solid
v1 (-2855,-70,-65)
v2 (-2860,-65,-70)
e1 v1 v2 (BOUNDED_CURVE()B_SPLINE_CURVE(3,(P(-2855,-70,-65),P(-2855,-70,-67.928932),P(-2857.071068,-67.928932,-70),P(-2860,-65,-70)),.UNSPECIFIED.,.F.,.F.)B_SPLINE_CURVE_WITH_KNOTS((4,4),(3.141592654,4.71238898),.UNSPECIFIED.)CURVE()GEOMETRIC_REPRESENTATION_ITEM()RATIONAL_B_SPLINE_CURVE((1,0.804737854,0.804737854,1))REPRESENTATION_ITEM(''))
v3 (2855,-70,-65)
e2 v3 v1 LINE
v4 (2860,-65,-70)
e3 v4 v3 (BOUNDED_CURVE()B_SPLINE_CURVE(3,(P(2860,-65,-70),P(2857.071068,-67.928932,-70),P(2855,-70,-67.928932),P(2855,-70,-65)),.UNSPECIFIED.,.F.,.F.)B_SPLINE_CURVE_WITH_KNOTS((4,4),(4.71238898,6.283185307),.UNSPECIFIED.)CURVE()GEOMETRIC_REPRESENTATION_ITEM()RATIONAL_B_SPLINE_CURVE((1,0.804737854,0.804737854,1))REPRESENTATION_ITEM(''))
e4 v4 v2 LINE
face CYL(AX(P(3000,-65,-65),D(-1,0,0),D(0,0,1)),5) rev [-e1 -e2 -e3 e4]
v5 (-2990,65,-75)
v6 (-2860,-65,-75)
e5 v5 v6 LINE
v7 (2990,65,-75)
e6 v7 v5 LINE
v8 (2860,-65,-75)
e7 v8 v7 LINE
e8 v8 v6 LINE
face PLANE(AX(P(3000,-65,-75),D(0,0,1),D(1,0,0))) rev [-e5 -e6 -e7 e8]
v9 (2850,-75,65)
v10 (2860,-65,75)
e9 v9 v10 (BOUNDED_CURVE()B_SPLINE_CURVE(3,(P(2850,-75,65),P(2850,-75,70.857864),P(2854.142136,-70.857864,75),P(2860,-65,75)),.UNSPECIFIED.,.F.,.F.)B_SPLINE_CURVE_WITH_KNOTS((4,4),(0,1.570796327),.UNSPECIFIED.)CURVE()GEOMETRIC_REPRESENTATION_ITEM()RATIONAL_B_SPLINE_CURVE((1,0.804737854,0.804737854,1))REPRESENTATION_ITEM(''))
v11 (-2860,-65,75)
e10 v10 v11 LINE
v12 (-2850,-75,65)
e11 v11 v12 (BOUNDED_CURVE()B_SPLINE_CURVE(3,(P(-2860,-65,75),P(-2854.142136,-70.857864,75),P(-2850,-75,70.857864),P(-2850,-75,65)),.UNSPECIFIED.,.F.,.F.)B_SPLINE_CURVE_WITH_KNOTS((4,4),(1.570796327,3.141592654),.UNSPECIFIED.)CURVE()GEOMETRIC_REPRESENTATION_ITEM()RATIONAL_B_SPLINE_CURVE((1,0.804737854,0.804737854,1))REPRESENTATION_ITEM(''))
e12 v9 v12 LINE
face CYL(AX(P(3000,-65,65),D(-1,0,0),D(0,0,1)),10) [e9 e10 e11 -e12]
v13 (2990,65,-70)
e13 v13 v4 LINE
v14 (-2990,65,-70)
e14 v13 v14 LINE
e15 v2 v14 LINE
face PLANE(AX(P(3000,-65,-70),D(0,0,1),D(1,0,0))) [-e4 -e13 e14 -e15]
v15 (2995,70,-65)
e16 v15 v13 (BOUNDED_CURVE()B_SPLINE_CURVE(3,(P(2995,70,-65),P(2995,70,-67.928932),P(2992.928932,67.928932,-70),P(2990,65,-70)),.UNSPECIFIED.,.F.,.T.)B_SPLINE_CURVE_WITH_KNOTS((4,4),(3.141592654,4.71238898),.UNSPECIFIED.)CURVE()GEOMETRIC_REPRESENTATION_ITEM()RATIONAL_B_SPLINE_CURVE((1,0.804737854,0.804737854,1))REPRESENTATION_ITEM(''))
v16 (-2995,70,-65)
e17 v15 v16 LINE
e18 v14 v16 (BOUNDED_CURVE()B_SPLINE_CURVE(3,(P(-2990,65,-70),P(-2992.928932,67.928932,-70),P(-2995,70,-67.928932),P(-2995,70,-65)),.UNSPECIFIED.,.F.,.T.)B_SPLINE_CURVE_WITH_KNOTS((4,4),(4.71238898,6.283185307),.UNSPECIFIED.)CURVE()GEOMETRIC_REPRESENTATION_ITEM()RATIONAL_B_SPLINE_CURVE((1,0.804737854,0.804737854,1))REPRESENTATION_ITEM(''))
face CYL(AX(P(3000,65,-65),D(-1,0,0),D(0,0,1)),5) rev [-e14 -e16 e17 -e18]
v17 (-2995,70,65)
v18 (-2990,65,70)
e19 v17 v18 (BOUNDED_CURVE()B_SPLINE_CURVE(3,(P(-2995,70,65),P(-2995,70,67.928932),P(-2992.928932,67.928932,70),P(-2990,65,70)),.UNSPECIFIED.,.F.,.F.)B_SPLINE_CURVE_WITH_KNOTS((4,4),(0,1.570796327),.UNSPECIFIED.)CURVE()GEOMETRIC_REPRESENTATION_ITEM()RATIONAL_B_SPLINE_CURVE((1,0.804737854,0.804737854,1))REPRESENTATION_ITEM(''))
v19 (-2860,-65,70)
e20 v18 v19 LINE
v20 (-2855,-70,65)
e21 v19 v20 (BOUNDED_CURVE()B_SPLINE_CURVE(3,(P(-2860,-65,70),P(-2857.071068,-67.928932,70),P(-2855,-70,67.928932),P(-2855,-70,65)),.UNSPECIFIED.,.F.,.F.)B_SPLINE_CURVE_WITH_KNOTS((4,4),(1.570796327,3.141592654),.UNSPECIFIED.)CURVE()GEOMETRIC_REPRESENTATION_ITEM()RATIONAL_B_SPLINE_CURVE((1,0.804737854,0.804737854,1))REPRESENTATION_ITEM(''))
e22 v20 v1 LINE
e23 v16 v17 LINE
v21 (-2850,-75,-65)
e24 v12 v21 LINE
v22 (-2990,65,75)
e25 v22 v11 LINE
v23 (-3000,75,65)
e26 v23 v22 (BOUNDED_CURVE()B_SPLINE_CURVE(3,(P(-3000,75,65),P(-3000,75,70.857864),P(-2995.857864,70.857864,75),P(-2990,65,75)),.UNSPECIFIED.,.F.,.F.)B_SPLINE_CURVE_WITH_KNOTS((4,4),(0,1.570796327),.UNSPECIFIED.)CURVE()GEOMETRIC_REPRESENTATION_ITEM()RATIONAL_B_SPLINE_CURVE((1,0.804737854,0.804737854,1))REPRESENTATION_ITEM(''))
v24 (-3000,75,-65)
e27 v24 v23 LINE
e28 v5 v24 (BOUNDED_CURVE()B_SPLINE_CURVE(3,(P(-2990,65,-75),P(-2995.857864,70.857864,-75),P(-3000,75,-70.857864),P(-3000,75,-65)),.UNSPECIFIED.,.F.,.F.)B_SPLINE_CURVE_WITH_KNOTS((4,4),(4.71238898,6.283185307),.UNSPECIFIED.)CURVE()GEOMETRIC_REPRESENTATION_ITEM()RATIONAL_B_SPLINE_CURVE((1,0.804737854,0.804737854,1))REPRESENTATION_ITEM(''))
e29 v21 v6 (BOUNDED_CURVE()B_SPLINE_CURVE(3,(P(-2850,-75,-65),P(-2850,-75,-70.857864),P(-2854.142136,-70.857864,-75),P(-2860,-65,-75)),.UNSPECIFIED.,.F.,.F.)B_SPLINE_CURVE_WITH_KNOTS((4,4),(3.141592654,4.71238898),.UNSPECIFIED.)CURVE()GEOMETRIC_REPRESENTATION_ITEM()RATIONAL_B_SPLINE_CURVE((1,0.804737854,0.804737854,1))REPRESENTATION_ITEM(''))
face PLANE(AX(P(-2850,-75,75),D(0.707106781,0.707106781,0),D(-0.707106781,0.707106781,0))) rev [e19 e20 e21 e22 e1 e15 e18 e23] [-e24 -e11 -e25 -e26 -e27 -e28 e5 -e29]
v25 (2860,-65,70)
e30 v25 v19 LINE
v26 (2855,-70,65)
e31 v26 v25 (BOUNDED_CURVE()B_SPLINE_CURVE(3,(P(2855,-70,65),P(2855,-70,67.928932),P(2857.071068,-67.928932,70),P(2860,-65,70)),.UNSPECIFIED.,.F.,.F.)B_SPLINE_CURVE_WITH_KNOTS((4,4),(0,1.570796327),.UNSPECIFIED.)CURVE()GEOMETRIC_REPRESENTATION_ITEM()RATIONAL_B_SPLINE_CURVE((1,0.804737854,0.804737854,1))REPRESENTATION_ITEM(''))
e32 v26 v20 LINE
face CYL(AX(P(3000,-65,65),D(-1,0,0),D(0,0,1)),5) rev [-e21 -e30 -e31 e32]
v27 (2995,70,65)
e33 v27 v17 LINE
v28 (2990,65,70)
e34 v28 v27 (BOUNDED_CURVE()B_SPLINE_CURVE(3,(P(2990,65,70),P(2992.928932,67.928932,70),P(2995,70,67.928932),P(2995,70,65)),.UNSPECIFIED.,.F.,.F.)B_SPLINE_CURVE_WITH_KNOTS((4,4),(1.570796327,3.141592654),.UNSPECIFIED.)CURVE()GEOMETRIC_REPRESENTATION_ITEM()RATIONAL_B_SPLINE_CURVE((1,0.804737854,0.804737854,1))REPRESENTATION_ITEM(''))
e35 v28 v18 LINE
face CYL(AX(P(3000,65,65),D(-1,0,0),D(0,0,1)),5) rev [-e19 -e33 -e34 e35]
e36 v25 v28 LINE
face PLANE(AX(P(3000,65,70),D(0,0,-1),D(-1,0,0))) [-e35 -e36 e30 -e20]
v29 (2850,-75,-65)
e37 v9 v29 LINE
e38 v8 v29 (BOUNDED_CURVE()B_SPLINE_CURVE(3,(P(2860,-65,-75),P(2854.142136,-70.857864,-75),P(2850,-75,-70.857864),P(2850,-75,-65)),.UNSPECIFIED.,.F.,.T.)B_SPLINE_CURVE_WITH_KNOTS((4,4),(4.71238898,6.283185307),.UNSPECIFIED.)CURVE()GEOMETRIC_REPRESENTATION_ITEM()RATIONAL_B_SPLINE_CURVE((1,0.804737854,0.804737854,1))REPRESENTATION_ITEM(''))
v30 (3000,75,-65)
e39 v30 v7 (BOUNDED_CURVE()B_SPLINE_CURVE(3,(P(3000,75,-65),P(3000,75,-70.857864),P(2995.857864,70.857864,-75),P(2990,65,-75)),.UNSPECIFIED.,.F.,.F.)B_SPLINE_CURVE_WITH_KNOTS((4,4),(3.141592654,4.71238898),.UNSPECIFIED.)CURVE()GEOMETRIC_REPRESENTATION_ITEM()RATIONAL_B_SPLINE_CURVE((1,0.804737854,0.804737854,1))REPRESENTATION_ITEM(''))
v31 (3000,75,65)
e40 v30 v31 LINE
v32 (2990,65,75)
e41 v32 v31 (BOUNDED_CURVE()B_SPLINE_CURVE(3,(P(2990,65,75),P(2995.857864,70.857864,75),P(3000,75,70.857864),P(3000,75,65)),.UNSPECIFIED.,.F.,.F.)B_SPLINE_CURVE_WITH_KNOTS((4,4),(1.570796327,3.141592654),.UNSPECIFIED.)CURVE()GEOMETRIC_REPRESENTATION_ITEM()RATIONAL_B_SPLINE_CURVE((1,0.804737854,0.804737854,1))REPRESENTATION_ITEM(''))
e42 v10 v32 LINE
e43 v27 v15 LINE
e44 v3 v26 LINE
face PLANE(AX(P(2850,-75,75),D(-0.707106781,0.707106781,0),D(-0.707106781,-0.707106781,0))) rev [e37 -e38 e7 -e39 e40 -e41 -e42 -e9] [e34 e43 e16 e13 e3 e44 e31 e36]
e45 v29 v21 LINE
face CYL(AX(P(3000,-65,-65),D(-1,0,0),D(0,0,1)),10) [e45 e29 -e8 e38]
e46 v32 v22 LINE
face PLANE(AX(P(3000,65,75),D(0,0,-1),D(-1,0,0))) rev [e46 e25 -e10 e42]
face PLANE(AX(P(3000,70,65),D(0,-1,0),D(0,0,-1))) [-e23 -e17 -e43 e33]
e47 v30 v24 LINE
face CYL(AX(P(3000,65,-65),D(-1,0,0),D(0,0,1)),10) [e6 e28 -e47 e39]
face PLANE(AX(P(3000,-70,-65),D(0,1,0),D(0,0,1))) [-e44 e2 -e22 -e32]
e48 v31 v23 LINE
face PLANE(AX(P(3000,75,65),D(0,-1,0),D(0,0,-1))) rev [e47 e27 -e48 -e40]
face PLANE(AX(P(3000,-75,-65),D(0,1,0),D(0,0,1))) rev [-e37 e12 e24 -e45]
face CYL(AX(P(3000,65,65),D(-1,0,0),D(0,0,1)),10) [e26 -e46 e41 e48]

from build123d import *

# Parameters (mm, degrees)
GB_6728_1986_150_X_150_X_5_1_DEPTH = 6000
CUT_EXTRUDE_1_DEPTH                = 3005.683843602


with BuildPart() as part:
    # Sketch1 → Gb／6728-1986方形空心型钢 150 X 150 X 5(1) (new body)
    with BuildSketch(Plane.YZ.offset(-3000)):
        with BuildLine():
            Line((-65, -75), (65, -75))
            ThreePointArc((65, -75), (72.071067812, -72.071067812), (75, -65))
            Line((75, -65), (75, 65))
            ThreePointArc((75, 65), (72.071067812, 72.071067812), (65, 75))
            Line((65, 75), (-65, 75))
            ThreePointArc((-65, 75), (-72.071067812, 72.071067812), (-75, 65))
            Line((-75, 65), (-75, -65))
            ThreePointArc((-75, -65), (-72.071067812, -72.071067812), (-65, -75))
        make_face()
        with BuildLine():
            Line((-65, -70), (65, -70))
            ThreePointArc((65, -70), (68.535533906, -68.535533906), (70, -65))
            Line((70, -65), (70, 65))
            ThreePointArc((70, 65), (68.535533906, 68.535533906), (65, 70))
            Line((65, 70), (-65, 70))
            ThreePointArc((-65, 70), (-68.535533906, 68.535533906), (-70, 65))
            Line((-70, 65), (-70, -65))
            ThreePointArc((-70, -65), (-68.535533906, -68.535533906), (-65, -70))
        make_face(mode=Mode.SUBTRACT)
    extrude(amount=GB_6728_1986_150_X_150_X_5_1_DEPTH)

    # 草图6 → 切除-拉伸1 (cut, through all)
    with BuildSketch(Plane(origin=(0, 0, -75), x_dir=(-1, 0, 0), z_dir=(0, 0, -1))):
        Polygon((3000, 75), (3000, -75), (2850, -75), align=None)
        Polygon((-2850, -75), (-3000, 75), (-3000, -75), align=None)
    extrude(amount=-CUT_EXTRUDE_1_DEPTH, mode=Mode.SUBTRACT)


solid = part.part
